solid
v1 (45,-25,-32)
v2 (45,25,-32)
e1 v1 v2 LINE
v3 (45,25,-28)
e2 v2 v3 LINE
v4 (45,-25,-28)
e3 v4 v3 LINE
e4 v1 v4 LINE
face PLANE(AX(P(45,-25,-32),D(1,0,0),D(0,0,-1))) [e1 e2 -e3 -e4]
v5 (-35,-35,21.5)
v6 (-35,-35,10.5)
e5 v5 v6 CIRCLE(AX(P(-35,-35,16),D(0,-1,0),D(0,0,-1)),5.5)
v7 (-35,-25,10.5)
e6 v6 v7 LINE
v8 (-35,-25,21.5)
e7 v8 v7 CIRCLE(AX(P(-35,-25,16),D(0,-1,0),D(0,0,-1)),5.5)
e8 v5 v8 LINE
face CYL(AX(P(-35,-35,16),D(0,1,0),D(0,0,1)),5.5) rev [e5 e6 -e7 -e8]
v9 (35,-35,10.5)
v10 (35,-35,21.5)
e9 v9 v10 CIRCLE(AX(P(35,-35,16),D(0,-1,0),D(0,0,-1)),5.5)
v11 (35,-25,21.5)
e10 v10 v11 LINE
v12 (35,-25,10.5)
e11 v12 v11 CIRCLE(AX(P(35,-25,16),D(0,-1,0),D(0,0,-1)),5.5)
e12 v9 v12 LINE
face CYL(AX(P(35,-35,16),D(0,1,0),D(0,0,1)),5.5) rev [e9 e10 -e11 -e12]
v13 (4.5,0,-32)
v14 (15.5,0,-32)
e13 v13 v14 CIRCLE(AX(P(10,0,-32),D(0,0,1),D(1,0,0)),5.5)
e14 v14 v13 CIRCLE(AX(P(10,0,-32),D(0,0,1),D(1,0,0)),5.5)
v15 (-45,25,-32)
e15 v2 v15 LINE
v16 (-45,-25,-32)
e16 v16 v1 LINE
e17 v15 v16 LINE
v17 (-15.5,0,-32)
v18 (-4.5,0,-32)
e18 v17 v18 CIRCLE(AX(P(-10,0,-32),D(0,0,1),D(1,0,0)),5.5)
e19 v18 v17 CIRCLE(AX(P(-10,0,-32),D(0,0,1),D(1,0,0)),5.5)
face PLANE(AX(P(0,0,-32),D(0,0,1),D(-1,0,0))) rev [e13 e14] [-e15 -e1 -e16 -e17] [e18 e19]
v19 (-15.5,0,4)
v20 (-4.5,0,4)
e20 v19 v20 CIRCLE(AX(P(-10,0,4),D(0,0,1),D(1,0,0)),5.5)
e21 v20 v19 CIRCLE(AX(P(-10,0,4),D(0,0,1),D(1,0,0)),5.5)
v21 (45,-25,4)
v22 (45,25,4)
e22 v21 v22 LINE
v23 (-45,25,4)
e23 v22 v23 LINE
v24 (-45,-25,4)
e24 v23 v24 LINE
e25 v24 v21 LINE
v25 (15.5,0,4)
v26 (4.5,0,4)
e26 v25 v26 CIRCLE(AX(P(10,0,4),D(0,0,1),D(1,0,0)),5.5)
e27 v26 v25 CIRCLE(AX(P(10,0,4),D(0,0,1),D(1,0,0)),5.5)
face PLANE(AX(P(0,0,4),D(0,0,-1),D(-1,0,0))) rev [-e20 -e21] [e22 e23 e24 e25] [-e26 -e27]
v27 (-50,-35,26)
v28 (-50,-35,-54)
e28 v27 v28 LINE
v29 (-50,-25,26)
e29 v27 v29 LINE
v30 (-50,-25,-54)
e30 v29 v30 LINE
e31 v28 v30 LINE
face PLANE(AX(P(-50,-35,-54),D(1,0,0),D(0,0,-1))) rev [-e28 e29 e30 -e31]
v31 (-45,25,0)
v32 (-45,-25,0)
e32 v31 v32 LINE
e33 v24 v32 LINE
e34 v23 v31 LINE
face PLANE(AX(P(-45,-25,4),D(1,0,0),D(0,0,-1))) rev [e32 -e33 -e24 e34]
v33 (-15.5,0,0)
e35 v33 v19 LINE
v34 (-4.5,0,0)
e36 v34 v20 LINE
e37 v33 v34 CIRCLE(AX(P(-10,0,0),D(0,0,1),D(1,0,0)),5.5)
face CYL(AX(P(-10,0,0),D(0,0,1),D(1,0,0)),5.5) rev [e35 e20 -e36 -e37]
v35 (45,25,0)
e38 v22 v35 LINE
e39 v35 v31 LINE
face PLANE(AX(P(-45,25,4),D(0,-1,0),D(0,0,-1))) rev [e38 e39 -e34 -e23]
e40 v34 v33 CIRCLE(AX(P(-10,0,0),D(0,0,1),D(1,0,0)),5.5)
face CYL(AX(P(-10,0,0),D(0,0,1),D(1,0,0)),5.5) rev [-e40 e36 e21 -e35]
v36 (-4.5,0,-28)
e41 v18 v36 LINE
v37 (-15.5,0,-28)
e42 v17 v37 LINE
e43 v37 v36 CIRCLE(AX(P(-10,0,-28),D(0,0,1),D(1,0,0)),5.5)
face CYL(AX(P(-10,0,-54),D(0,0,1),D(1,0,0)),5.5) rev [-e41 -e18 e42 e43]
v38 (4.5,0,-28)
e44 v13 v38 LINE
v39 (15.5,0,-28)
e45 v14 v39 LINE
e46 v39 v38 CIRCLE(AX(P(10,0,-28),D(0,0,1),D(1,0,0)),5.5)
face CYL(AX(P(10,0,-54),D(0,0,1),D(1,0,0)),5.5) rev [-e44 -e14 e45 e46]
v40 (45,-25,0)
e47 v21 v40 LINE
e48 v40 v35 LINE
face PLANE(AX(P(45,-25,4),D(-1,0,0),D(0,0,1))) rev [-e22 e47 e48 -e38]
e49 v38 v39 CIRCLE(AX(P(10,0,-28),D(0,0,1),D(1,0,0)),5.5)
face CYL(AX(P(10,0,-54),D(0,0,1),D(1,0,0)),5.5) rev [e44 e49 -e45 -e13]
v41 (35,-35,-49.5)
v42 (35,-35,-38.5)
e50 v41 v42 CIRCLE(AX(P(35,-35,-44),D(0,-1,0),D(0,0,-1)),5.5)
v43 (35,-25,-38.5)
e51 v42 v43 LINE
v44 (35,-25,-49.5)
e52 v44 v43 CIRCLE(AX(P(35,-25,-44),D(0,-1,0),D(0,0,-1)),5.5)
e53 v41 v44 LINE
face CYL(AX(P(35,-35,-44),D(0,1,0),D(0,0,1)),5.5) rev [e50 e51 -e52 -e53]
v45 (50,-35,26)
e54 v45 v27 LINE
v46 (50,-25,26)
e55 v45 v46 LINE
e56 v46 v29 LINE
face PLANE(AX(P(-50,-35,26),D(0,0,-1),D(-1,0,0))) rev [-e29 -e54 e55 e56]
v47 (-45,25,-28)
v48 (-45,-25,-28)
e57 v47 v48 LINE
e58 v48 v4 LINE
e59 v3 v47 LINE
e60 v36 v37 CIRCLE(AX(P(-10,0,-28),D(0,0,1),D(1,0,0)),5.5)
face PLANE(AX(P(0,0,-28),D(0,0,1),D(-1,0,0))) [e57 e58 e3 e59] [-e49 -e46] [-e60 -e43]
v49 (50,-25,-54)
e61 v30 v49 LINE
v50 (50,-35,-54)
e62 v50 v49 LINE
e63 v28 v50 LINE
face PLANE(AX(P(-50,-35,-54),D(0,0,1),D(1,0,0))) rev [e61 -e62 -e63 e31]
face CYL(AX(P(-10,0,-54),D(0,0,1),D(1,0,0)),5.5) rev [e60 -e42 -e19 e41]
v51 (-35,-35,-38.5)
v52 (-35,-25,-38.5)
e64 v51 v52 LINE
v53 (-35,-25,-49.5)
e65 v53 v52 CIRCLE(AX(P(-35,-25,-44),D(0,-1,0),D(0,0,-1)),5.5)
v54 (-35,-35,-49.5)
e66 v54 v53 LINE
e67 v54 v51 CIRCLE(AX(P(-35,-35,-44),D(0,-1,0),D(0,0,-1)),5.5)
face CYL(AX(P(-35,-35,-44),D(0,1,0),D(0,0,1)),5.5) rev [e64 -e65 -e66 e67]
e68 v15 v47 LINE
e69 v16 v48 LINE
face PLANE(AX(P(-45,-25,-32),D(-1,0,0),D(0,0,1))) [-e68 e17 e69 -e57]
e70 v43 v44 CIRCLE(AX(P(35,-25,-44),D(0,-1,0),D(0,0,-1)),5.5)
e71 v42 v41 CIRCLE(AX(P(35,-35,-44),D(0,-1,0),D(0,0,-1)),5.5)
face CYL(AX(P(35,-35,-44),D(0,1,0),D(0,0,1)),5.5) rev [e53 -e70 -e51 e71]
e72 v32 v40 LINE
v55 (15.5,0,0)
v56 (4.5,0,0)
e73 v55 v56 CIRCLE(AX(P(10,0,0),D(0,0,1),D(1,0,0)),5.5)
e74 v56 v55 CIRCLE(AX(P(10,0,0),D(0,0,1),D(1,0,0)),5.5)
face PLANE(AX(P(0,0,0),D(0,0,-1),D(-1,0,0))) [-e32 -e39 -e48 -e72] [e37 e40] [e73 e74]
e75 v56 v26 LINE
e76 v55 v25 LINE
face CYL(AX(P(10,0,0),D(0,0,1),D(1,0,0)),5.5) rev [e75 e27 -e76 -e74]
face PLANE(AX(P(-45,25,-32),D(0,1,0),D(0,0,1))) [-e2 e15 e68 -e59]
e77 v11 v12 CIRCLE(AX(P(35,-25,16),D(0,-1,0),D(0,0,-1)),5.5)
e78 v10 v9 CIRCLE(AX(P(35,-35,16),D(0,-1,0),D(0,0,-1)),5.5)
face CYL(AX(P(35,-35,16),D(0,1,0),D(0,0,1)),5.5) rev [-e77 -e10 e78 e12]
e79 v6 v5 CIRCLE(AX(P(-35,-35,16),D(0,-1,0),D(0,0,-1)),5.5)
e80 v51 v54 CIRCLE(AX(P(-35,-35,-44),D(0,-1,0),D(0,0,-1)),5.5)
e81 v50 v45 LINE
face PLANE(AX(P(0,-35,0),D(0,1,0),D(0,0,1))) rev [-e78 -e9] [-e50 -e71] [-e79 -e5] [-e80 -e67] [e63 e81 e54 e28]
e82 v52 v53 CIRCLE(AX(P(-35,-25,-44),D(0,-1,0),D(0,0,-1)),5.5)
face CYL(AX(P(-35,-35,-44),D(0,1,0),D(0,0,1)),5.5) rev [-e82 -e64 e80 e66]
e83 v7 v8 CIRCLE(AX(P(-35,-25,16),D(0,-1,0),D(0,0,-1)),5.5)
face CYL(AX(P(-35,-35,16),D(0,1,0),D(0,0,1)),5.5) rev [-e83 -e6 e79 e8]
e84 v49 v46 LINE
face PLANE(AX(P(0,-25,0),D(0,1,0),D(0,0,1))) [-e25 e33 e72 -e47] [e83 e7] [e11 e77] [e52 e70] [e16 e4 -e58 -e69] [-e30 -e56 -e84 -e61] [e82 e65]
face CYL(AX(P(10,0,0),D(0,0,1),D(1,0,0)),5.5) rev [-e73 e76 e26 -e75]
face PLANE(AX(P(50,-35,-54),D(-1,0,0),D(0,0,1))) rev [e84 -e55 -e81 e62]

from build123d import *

# Parameters (mm, degrees)
SKETCH_1_W          = 90
SKETCH_1_H          = 50
EXTRUDE_1_DEPTH     = 4
SKETCH_2_R          = 5.5
CUT_EXTRUDE_1_DEPTH = 52.633322574
SKETCH_3_W          = 100
SKETCH_3_H          = 80
SKETCH_3_R          = 5.5
EXTRUDE_2_DEPTH     = 10
SKETCH_4_R          = 5.5
CUT_EXTRUDE_2_DEPTH = 82.492330928


with BuildPart() as part:
    # 草图1 → 凸台-拉伸1 (new body)
    with BuildSketch(Plane.XY):
        Rectangle(SKETCH_1_W, SKETCH_1_H)
    extrude_1 = extrude(amount=EXTRUDE_1_DEPTH)

    # 草图2 → 切除-拉伸1 (cut, through all)
    with BuildSketch(Plane.XY.offset(4)):
        with Locations((-10, 0)):
            Circle(SKETCH_2_R)
        with Locations((10, 0)):
            Circle(SKETCH_2_R)
    extrude(amount=-CUT_EXTRUDE_1_DEPTH, mode=Mode.SUBTRACT)

    # 草图3 → 凸台-拉伸2 (add)
    with BuildSketch(Plane.XZ.offset(25)):
        with Locations((0, -14)):
            Rectangle(SKETCH_3_W, SKETCH_3_H)
        with Locations(Location((-35, 16, 0), (0, 0, 270))):
            Circle(SKETCH_3_R, mode=Mode.SUBTRACT)
        with Locations(Location((35, 16, 0), (0, 0, 270))):
            Circle(SKETCH_3_R, mode=Mode.SUBTRACT)
        with Locations(Location((35, -44, 0), (0, 0, 270))):
            Circle(SKETCH_3_R, mode=Mode.SUBTRACT)
        with Locations(Location((-35, -44, 0), (0, 0, 270))):
            Circle(SKETCH_3_R, mode=Mode.SUBTRACT)
    extrude(amount=EXTRUDE_2_DEPTH)

    # 镜向1: 凸台-拉伸1 across plane
    add(extrude_1.mirror(Plane(origin=(0, 0, -14), x_dir=(1, 0, 0), z_dir=(0, 0, -1))))

    # 草图4 → 切除-拉伸2 (cut, through all)
    with BuildSketch(Plane.XY.offset(-28)):
        with Locations((-10, 0)):
            Circle(SKETCH_4_R)
        with Locations((10, 0)):
            Circle(SKETCH_4_R)
    extrude(amount=-CUT_EXTRUDE_2_DEPTH, mode=Mode.SUBTRACT)


solid = part.part
